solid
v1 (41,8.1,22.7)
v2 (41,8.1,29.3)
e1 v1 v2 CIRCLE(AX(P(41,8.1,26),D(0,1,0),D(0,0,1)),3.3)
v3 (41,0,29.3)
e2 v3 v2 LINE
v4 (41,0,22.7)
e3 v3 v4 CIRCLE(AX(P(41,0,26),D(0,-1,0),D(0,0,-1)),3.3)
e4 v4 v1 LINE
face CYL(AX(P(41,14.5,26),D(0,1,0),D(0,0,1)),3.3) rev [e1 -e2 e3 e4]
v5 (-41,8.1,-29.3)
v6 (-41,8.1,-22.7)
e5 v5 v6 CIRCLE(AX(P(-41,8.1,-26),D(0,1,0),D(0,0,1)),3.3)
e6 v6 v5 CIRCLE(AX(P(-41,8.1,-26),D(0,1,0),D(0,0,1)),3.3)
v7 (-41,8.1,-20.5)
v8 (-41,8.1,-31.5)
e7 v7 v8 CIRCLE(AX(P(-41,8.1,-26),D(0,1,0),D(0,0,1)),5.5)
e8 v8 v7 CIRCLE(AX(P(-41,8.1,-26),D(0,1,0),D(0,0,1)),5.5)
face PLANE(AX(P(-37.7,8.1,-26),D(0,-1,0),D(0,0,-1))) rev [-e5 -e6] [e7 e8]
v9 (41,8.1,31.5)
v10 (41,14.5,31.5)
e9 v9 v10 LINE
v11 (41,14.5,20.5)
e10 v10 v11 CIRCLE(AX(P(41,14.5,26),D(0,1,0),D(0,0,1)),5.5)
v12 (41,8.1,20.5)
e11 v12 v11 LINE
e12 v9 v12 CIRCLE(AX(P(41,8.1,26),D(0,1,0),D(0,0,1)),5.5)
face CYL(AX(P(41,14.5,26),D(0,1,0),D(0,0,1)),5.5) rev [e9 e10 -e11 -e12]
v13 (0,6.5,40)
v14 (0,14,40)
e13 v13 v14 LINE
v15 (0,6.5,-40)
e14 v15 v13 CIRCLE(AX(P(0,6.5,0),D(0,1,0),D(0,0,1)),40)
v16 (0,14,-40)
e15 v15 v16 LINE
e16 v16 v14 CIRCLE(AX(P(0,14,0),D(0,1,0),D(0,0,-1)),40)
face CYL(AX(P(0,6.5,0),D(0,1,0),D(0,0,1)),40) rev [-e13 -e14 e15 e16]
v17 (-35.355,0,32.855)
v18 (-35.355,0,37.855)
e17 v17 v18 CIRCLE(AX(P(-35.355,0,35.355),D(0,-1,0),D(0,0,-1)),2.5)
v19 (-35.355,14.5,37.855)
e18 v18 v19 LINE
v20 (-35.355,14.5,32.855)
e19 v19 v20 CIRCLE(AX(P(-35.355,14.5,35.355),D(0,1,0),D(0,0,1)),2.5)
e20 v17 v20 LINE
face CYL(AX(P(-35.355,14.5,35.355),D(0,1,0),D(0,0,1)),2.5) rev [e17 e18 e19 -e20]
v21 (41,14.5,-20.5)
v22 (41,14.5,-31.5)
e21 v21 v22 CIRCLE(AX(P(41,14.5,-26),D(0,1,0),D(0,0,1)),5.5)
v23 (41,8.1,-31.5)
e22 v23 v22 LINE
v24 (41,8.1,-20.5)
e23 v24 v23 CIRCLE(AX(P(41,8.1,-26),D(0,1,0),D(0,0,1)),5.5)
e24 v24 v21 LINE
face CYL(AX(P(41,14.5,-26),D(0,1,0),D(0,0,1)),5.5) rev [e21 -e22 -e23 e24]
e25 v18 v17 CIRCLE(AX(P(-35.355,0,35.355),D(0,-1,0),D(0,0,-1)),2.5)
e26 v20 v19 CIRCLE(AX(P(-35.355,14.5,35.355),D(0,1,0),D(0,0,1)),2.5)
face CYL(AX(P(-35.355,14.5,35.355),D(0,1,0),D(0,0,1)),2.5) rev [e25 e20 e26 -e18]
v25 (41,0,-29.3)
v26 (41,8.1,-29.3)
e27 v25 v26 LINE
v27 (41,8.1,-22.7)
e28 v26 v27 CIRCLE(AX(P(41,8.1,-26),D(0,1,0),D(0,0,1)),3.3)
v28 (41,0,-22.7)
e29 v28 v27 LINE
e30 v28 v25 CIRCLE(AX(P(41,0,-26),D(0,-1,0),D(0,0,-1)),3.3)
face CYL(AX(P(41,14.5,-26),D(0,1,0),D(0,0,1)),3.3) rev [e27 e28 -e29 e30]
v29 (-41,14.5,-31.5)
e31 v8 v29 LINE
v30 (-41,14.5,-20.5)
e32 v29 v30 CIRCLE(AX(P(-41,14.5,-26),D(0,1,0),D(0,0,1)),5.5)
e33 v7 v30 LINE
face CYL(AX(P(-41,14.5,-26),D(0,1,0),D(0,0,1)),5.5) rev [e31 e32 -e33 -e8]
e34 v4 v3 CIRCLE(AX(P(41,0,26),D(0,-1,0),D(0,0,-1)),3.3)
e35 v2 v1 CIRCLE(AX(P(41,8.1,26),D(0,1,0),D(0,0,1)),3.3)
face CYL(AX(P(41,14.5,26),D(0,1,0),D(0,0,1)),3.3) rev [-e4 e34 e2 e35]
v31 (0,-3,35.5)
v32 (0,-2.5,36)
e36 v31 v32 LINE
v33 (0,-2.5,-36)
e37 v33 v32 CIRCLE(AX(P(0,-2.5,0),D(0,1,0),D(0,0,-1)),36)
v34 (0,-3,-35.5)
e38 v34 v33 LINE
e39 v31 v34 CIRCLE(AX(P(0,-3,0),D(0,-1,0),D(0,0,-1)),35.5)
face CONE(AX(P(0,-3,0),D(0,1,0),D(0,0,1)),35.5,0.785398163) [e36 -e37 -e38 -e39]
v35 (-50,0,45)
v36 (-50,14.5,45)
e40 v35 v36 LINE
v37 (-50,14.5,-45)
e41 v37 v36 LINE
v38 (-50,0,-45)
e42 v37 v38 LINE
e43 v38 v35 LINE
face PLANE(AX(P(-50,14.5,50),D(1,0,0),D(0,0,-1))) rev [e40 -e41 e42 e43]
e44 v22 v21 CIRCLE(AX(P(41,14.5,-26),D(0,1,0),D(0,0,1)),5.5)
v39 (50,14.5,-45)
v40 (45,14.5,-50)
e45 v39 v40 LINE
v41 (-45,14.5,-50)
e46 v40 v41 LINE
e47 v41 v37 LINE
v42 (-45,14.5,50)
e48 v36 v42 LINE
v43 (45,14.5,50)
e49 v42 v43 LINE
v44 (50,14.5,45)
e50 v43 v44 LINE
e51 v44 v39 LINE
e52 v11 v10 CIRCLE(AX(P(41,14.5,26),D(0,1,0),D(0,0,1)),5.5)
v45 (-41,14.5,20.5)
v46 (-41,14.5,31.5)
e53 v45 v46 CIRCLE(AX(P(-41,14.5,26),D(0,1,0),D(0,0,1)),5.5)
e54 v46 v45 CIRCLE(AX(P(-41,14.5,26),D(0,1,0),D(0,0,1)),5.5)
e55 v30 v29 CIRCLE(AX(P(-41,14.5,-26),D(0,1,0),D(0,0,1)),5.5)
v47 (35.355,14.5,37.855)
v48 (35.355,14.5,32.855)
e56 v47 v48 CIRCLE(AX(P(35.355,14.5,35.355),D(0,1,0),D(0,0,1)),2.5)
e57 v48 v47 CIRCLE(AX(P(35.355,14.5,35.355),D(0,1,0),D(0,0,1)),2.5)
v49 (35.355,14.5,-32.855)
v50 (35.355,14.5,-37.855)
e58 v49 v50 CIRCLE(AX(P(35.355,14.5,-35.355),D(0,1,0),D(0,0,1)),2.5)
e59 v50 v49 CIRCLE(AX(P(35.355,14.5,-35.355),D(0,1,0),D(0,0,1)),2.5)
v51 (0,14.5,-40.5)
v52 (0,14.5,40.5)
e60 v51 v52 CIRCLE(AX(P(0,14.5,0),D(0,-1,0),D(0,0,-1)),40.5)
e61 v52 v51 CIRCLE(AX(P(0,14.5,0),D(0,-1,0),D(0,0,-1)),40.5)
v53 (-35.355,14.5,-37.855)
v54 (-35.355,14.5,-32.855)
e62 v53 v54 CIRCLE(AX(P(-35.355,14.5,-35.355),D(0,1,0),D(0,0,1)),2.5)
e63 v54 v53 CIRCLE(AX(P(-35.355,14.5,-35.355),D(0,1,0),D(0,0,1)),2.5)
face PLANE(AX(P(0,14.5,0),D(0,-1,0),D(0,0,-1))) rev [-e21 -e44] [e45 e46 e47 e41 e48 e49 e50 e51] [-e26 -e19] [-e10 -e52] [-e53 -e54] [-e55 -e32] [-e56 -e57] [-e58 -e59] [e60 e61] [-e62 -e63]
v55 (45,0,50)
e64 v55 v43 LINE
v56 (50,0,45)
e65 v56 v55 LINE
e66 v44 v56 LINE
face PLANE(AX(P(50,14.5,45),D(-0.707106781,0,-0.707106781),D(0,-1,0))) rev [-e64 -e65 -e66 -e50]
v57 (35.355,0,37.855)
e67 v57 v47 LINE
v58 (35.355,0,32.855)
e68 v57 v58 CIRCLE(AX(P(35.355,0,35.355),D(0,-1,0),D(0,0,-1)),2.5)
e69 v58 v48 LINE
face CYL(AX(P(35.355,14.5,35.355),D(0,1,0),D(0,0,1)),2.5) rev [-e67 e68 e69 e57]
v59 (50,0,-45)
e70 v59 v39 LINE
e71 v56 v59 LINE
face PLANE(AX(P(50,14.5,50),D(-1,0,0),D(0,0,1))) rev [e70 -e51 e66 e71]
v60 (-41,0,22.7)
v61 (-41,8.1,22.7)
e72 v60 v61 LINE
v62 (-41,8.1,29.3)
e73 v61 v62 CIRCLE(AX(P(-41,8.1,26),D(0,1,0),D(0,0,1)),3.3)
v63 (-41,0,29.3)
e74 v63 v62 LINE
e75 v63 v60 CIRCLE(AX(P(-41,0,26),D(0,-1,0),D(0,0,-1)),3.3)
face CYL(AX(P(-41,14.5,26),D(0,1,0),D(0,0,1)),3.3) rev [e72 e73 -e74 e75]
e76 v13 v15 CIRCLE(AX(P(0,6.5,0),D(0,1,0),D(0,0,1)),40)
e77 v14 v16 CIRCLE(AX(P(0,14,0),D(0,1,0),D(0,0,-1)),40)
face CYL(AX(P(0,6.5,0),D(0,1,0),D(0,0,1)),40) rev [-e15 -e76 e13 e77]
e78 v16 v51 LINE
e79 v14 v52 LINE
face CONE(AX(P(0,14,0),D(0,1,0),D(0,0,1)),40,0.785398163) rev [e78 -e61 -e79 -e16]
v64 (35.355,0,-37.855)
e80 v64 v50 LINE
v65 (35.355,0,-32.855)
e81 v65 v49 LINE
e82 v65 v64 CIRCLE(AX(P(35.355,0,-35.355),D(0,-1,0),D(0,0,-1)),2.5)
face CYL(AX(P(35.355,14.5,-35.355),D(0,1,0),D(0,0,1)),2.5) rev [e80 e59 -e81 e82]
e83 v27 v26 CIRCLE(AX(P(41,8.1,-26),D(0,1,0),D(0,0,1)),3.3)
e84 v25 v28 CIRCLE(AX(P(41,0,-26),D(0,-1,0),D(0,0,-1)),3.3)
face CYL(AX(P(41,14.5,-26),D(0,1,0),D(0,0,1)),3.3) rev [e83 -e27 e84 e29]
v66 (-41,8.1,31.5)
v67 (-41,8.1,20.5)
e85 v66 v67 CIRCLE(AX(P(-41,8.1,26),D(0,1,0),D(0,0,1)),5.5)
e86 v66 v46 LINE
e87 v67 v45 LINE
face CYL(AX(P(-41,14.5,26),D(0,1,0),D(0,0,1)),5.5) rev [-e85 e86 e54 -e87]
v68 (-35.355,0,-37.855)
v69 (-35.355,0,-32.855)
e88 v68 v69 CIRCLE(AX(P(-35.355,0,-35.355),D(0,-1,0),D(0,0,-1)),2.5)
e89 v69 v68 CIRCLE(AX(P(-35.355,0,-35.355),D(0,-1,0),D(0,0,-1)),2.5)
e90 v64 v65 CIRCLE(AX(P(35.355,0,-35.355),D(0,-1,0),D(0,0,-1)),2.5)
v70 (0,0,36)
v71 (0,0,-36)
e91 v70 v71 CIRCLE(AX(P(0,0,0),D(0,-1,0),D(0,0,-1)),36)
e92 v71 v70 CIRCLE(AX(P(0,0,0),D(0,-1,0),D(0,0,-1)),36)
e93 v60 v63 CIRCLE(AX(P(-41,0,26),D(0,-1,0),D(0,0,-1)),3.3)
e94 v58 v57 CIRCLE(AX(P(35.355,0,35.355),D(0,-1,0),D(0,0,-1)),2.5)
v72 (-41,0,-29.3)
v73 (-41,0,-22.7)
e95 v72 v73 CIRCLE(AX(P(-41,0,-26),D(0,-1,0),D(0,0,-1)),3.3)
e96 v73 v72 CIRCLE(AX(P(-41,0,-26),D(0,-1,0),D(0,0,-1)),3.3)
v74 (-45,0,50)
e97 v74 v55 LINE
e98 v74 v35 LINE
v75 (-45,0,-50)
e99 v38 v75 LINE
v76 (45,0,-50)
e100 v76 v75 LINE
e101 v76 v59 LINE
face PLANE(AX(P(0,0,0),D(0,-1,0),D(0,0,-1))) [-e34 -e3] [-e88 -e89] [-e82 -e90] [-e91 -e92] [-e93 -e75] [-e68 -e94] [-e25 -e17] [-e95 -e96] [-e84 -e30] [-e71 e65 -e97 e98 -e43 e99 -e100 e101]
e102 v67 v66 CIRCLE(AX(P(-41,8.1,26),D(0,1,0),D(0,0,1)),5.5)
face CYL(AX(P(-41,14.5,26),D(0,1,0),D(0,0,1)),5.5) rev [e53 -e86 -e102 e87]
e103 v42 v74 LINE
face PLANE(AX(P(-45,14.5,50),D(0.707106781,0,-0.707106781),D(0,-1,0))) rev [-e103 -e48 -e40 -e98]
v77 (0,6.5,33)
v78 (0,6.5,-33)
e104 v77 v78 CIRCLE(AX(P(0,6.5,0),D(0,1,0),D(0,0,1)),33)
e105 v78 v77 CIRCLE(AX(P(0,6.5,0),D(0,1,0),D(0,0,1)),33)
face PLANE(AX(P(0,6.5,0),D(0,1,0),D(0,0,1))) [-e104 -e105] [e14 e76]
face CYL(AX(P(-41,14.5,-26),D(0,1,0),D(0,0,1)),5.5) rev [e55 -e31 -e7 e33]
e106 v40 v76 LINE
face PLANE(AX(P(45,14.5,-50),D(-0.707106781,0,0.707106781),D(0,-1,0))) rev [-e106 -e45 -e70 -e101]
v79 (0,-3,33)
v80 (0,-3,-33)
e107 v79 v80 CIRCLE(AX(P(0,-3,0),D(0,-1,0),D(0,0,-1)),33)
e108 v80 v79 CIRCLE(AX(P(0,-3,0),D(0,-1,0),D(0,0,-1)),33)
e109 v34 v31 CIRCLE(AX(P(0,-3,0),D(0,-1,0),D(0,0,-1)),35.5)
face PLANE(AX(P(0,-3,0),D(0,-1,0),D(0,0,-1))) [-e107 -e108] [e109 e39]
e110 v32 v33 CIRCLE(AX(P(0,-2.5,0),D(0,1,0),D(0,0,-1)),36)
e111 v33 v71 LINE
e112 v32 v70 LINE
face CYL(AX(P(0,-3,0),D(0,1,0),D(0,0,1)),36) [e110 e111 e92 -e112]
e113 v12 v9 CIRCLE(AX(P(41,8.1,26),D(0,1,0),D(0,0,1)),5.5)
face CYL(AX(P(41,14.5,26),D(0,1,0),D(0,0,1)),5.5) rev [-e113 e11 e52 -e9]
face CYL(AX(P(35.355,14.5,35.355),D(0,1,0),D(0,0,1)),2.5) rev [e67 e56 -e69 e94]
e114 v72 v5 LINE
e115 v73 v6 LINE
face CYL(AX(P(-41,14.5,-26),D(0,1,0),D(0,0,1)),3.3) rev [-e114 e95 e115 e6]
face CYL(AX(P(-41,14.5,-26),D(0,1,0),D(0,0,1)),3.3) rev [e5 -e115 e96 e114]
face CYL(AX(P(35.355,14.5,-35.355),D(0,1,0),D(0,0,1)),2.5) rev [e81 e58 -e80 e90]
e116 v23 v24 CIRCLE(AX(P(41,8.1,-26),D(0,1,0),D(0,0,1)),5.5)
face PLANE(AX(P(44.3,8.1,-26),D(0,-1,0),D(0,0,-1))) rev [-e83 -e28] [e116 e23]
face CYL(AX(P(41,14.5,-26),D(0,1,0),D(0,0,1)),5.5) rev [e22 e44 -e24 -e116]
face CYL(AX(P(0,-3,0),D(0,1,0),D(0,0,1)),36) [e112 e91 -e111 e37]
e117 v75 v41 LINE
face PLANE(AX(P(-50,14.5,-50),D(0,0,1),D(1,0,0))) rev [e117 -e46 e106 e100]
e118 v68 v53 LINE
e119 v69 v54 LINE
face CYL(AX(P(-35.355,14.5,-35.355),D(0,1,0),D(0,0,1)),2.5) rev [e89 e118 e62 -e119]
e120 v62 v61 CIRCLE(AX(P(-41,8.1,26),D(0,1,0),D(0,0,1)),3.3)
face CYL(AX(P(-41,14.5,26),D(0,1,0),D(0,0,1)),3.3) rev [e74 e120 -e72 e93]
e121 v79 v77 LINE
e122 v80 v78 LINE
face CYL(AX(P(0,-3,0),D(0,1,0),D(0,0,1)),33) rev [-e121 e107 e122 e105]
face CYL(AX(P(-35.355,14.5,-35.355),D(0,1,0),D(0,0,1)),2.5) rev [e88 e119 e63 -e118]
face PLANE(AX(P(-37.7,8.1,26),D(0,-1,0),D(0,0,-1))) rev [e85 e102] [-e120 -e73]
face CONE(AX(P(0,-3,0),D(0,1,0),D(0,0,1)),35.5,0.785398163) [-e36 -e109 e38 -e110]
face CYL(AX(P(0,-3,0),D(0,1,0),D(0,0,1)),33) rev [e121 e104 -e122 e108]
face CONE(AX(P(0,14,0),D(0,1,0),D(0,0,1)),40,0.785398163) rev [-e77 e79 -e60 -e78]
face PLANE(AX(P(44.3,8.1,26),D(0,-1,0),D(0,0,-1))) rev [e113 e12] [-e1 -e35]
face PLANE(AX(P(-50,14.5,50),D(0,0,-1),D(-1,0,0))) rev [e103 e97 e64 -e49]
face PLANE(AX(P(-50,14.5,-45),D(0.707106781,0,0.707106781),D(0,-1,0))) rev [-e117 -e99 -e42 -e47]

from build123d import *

# Parameters (mm, degrees)
SKETCH_1_W                   = 100
SKETCH_1_H                   = 100
EXTRUDE_1_DEPTH              = 14.5
SKETCH_3_R                   = 36
SKETCH_3_R_2                 = 33
EXTRUDE_2_DEPTH              = 3
SKETCH_4_R                   = 33
CUT_EXTRUDE_1_DEPTH          = 73.182061483
CHAMFER_1_SIZE               = 5
CHAMFER_2_SIZE               = 0.5
SKETCH_10_R                  = 40
CUT_EXTRUDE_3_DEPTH          = 8
HOLE_WIZARD_M6_1_D           = 5
HOLE_WIZARD_M6_1_DEPTH       = 15
HOLE_WIZARD_M6_1_TIP         = 1.502151548
HOLE_WIZARD_M6_2_D           = 6.6
HOLE_WIZARD_M6_2_CBORE_D     = 11
HOLE_WIZARD_M6_2_CBORE_DEPTH = 6.4
CHAMFER_3_SIZE               = 0.5


with BuildPart() as part:
    # 草图1 → 凸台-拉伸1 (new body)
    with BuildSketch(Plane(origin=(0, 0, 0), x_dir=(1, 0, 0), z_dir=(0, 1, 0))):
        Rectangle(SKETCH_1_W, SKETCH_1_H)
    extrude(amount=EXTRUDE_1_DEPTH)

    # 草图3 → 凸台-拉伸2 (add)
    with BuildSketch(Plane.XZ):
        with Locations(Location((0, 0, 0), (0, 0, 270))):
            Circle(SKETCH_3_R)
        with Locations(Location((0, 0, 0), (0, 0, 270))):
            Circle(SKETCH_3_R_2, mode=Mode.SUBTRACT)
    extrude(amount=EXTRUDE_2_DEPTH)

    # 草图4 → 切除-拉伸1 (cut, through all)
    with BuildSketch(Plane.XZ):
        with Locations(Location((0, 0, 0), (0, 0, 270))):
            Circle(SKETCH_4_R)
    extrude(amount=-CUT_EXTRUDE_1_DEPTH, mode=Mode.SUBTRACT)

    # 倒角1
    chamfer_1_edges = [part.edges().sort_by_distance(p)[0] for p in [
        (50, 7.25, 50),
        (-50, 7.25, 50),
        (-50, 7.25, -50),
        (50, 7.25, -50),
    ]]
    chamfer(chamfer_1_edges, length=CHAMFER_1_SIZE)

    # 倒角2
    chamfer_2_edges = [part.edges().sort_by_distance(p)[0] for p in [
        (0, -3, 36),
    ]]
    chamfer(chamfer_2_edges, length=CHAMFER_2_SIZE)

    # 草图10 → 切除-拉伸3 (cut)
    with BuildSketch(Plane(origin=(0, 14.5, 0), x_dir=(1, 0, 0), z_dir=(0, 1, 0))):
        with Locations(Location((0, 0, 0), (0, 0, 270))):
            Circle(SKETCH_10_R)
    extrude(amount=-CUT_EXTRUDE_3_DEPTH, mode=Mode.SUBTRACT)

    # Hole Wizard M6 _1
    with Locations(Plane(origin=(0, 14.5, 0), x_dir=(1, 0, 0), z_dir=(0, 1, 0))):
        with Locations((-35.355, 35.355), (0, 0), (35.355, 35.355), (-35.355, -35.355), (35.355, -35.355)):
            Hole(HOLE_WIZARD_M6_1_D / 2, depth=HOLE_WIZARD_M6_1_DEPTH)
            with Locations((0, 0, -(HOLE_WIZARD_M6_1_DEPTH + HOLE_WIZARD_M6_1_TIP / 2))):  # 118° drill point
                Cone(0, HOLE_WIZARD_M6_1_D / 2, HOLE_WIZARD_M6_1_TIP, mode=Mode.SUBTRACT)

    # M6 六角凹头螺钉的柱形沉头孔2 (through all)
    with Locations(Plane(origin=(0, 14.5, 0), x_dir=(1, 0, 0), z_dir=(0, 1, 0))):
        with Locations((-41, 26), (0, 0), (41, -26), (41, 26), (-41, -26)):
            CounterBoreHole(HOLE_WIZARD_M6_2_D / 2, HOLE_WIZARD_M6_2_CBORE_D / 2, HOLE_WIZARD_M6_2_CBORE_DEPTH)

    # 倒角3
    chamfer_3_edges = [part.edges().sort_by_distance(p)[0] for p in [
        (0, 14.5, -40),
    ]]
    chamfer(chamfer_3_edges, length=CHAMFER_3_SIZE)


solid = part.part
